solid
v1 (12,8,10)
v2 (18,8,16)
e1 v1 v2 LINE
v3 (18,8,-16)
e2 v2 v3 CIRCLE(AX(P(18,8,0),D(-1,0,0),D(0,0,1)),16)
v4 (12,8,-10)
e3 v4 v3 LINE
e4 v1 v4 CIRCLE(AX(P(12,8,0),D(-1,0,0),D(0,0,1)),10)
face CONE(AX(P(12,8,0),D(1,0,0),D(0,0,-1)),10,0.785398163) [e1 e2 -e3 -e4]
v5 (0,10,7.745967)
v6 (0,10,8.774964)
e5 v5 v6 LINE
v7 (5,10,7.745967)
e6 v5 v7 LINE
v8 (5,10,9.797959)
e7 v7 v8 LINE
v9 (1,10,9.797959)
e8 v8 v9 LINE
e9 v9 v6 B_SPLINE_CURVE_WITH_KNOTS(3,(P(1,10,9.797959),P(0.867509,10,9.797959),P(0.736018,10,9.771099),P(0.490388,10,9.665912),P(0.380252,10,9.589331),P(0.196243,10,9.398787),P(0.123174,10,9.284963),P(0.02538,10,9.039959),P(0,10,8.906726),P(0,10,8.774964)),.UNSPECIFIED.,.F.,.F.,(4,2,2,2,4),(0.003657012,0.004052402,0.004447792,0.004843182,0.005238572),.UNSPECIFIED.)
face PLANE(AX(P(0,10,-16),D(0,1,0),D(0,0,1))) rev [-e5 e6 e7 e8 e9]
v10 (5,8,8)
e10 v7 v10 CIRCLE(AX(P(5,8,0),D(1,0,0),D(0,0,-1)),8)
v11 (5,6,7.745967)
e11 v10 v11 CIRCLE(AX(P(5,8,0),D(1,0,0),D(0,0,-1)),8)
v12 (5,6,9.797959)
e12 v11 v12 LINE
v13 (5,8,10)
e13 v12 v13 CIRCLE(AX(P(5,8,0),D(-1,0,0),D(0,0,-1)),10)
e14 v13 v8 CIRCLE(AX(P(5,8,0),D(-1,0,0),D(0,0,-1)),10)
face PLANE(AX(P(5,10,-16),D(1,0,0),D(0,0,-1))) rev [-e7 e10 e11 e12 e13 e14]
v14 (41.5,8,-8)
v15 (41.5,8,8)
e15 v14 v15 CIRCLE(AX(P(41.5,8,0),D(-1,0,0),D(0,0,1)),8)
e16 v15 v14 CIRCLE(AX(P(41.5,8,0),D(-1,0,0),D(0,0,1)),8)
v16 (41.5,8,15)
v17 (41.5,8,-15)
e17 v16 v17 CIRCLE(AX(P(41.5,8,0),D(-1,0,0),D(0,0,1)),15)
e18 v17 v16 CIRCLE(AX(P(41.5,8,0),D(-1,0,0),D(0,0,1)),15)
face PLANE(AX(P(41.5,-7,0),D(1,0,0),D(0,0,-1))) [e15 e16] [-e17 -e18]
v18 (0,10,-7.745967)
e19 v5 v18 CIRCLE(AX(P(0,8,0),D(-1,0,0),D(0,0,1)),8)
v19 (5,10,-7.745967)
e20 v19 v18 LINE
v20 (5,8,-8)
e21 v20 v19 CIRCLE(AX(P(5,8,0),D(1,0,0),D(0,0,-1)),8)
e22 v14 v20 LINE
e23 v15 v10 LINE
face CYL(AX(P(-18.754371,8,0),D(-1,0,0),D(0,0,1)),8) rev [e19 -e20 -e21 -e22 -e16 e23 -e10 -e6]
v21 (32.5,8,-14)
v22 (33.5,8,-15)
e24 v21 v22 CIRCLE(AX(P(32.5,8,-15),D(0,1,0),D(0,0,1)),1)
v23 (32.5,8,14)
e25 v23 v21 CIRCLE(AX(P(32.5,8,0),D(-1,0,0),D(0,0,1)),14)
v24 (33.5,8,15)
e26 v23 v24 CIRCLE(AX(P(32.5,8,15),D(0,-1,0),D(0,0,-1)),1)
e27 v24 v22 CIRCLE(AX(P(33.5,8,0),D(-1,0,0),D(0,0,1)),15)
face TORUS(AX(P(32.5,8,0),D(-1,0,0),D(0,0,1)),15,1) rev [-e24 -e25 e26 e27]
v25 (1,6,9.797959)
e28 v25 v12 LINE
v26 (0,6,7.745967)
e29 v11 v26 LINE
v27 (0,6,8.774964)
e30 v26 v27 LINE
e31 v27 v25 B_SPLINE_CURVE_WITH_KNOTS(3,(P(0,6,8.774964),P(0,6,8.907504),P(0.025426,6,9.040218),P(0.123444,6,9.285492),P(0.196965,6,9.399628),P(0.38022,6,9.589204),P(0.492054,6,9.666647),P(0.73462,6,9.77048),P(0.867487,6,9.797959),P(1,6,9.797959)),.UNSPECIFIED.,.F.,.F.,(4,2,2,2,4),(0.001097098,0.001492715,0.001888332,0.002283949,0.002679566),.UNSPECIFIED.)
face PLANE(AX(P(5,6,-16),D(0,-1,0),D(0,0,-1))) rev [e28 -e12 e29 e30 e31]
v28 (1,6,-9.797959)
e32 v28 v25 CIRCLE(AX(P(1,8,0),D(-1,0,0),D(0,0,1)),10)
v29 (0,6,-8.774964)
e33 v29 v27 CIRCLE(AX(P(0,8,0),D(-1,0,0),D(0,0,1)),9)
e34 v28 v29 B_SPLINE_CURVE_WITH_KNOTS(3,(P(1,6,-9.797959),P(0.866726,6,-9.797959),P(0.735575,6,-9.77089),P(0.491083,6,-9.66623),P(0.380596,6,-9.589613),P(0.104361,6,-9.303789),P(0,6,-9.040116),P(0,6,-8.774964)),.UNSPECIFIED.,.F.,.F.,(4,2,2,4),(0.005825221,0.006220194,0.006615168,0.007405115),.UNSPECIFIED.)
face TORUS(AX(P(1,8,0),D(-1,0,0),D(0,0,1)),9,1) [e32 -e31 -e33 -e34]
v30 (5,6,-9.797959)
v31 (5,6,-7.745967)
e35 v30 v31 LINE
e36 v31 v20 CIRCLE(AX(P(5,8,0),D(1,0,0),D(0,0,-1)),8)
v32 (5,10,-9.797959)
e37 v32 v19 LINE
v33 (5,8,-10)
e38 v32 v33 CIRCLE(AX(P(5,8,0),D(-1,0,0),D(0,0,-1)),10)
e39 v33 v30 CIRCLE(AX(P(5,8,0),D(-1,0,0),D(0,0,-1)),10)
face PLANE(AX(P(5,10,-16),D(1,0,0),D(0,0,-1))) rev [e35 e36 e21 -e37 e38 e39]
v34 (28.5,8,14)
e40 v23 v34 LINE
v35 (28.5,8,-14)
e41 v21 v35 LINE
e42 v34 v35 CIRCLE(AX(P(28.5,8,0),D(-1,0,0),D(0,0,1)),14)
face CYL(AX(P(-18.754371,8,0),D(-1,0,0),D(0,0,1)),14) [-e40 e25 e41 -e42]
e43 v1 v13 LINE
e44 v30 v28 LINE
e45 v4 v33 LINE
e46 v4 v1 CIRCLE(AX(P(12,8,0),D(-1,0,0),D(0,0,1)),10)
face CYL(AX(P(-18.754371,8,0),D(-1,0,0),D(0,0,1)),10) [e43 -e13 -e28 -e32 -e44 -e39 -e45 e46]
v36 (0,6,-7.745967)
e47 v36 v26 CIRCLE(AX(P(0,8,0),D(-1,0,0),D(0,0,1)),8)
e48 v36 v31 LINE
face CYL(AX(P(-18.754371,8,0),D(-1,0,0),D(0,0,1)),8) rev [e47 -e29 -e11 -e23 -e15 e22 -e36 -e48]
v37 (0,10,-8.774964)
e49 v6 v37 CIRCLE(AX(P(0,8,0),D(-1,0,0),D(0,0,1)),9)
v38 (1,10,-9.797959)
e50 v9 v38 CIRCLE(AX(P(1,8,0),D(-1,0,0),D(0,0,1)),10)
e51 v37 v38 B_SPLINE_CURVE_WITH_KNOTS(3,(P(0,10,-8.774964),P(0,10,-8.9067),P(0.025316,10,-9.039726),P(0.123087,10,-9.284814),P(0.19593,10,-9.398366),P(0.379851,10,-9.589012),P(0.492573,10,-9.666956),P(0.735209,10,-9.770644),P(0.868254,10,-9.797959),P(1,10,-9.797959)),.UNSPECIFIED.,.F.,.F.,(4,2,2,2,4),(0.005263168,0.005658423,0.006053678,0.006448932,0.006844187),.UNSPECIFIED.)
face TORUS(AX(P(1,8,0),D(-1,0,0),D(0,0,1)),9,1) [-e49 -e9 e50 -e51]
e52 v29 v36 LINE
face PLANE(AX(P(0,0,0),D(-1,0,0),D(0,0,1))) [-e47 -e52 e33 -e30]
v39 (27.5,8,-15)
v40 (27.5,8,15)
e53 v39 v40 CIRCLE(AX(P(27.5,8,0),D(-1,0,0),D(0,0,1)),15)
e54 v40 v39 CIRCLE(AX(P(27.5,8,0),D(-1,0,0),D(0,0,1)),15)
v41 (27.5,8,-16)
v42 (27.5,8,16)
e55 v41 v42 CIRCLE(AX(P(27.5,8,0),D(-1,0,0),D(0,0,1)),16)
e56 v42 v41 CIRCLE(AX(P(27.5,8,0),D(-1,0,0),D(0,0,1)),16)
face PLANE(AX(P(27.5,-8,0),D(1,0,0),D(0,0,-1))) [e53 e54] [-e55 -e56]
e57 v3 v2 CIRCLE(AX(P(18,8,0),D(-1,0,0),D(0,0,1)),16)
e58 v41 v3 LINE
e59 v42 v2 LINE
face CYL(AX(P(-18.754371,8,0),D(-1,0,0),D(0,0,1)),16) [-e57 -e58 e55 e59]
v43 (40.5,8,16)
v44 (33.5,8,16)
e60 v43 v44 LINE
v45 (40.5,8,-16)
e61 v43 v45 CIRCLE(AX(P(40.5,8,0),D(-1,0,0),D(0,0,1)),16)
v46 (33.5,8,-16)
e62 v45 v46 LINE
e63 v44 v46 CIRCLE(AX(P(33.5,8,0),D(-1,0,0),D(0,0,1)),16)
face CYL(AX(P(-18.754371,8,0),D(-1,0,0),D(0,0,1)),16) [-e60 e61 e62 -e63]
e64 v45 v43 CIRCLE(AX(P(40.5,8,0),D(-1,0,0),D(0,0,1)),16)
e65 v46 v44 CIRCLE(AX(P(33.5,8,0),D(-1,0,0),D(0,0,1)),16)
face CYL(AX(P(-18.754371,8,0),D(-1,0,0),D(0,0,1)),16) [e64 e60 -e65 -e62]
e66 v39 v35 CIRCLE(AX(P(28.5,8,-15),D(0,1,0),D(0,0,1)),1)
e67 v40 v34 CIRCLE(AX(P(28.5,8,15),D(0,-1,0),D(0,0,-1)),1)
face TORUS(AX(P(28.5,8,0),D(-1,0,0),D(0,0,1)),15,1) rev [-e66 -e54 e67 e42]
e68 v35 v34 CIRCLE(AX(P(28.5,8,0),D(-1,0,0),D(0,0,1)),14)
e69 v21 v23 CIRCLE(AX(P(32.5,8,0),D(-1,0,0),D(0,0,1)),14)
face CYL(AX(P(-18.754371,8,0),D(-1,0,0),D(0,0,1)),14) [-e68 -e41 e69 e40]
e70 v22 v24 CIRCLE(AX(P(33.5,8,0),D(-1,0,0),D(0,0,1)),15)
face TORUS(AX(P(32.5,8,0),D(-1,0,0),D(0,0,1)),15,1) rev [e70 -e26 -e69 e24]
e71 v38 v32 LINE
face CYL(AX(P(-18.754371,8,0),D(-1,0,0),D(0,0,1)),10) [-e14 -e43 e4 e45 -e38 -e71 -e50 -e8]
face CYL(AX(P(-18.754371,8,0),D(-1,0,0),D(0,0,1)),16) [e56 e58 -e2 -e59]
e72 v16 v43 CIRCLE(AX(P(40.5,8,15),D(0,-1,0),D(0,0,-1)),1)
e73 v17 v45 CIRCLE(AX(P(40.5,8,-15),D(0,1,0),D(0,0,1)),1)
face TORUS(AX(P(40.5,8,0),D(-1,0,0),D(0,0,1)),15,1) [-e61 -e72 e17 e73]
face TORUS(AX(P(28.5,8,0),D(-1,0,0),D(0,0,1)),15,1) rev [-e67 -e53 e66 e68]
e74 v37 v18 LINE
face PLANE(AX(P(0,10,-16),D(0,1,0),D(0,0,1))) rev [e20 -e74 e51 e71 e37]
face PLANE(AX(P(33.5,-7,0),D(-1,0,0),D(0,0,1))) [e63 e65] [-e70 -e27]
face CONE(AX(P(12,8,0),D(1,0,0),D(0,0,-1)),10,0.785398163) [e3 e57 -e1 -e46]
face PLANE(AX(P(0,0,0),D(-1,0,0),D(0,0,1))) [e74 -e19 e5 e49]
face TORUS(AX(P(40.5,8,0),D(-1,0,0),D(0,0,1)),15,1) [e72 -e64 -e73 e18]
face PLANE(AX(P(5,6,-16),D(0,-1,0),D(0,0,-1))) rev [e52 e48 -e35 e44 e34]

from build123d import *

# Parameters (mm, degrees)
END_SLOT_CUT_DEPTH      = 51.539588475
END_SLOT_CUT_DEPTH_BACK = 51.539588475
END_SLOT_PROFILE_W      = 5
END_SLOT_PROFILE_H      = 4


with BuildPart() as part:
    # Bushing Revolve Profile → Stepped Bushing Body (revolve)
    with BuildSketch(Plane.XY, mode=Mode.PRIVATE) as stepped_bushing_body_sk:
        with BuildLine():
            Line((0, 0), (0, -1))
            ThreePointArc((0, -1), (0.292893219, -1.707106781), (1, -2))
            Line((1, -2), (12, -2))
            Line((12, -2), (18, -8))
            Line((18, -8), (27.5, -8))
            Line((27.5, -8), (27.5, -7))
            ThreePointArc((27.5, -7), (27.792893219, -6.292893219), (28.5, -6))
            Line((28.5, -6), (32.5, -6))
            ThreePointArc((32.5, -6), (33.207106781, -6.292893219), (33.5, -7))
            Line((33.5, -7), (33.5, -8))
            Line((33.5, -8), (40.5, -8))
            ThreePointArc((40.5, -8), (41.207106781, -7.707106781), (41.5, -7))
            Line((41.5, -7), (41.5, 0))
            Line((41.5, 0), (0, 0))
        make_face()
    revolve(stepped_bushing_body_sk.sketch.rotate(Axis((-18.754371045, 8, 0), (1, 0, 0)), 270), axis=Axis((-18.754371045, 8, 0), (1, 0, 0)))

    # End Slot Profile → End Slot Cut (cut, two sides: drawn at the far end of the back side and taken through both)
    with BuildSketch(Plane.XY.offset(-END_SLOT_CUT_DEPTH_BACK)):
        with Locations((2.5, 8)):
            Rectangle(END_SLOT_PROFILE_W, END_SLOT_PROFILE_H)
    extrude(amount=END_SLOT_CUT_DEPTH + END_SLOT_CUT_DEPTH_BACK, mode=Mode.SUBTRACT)


solid = part.part
